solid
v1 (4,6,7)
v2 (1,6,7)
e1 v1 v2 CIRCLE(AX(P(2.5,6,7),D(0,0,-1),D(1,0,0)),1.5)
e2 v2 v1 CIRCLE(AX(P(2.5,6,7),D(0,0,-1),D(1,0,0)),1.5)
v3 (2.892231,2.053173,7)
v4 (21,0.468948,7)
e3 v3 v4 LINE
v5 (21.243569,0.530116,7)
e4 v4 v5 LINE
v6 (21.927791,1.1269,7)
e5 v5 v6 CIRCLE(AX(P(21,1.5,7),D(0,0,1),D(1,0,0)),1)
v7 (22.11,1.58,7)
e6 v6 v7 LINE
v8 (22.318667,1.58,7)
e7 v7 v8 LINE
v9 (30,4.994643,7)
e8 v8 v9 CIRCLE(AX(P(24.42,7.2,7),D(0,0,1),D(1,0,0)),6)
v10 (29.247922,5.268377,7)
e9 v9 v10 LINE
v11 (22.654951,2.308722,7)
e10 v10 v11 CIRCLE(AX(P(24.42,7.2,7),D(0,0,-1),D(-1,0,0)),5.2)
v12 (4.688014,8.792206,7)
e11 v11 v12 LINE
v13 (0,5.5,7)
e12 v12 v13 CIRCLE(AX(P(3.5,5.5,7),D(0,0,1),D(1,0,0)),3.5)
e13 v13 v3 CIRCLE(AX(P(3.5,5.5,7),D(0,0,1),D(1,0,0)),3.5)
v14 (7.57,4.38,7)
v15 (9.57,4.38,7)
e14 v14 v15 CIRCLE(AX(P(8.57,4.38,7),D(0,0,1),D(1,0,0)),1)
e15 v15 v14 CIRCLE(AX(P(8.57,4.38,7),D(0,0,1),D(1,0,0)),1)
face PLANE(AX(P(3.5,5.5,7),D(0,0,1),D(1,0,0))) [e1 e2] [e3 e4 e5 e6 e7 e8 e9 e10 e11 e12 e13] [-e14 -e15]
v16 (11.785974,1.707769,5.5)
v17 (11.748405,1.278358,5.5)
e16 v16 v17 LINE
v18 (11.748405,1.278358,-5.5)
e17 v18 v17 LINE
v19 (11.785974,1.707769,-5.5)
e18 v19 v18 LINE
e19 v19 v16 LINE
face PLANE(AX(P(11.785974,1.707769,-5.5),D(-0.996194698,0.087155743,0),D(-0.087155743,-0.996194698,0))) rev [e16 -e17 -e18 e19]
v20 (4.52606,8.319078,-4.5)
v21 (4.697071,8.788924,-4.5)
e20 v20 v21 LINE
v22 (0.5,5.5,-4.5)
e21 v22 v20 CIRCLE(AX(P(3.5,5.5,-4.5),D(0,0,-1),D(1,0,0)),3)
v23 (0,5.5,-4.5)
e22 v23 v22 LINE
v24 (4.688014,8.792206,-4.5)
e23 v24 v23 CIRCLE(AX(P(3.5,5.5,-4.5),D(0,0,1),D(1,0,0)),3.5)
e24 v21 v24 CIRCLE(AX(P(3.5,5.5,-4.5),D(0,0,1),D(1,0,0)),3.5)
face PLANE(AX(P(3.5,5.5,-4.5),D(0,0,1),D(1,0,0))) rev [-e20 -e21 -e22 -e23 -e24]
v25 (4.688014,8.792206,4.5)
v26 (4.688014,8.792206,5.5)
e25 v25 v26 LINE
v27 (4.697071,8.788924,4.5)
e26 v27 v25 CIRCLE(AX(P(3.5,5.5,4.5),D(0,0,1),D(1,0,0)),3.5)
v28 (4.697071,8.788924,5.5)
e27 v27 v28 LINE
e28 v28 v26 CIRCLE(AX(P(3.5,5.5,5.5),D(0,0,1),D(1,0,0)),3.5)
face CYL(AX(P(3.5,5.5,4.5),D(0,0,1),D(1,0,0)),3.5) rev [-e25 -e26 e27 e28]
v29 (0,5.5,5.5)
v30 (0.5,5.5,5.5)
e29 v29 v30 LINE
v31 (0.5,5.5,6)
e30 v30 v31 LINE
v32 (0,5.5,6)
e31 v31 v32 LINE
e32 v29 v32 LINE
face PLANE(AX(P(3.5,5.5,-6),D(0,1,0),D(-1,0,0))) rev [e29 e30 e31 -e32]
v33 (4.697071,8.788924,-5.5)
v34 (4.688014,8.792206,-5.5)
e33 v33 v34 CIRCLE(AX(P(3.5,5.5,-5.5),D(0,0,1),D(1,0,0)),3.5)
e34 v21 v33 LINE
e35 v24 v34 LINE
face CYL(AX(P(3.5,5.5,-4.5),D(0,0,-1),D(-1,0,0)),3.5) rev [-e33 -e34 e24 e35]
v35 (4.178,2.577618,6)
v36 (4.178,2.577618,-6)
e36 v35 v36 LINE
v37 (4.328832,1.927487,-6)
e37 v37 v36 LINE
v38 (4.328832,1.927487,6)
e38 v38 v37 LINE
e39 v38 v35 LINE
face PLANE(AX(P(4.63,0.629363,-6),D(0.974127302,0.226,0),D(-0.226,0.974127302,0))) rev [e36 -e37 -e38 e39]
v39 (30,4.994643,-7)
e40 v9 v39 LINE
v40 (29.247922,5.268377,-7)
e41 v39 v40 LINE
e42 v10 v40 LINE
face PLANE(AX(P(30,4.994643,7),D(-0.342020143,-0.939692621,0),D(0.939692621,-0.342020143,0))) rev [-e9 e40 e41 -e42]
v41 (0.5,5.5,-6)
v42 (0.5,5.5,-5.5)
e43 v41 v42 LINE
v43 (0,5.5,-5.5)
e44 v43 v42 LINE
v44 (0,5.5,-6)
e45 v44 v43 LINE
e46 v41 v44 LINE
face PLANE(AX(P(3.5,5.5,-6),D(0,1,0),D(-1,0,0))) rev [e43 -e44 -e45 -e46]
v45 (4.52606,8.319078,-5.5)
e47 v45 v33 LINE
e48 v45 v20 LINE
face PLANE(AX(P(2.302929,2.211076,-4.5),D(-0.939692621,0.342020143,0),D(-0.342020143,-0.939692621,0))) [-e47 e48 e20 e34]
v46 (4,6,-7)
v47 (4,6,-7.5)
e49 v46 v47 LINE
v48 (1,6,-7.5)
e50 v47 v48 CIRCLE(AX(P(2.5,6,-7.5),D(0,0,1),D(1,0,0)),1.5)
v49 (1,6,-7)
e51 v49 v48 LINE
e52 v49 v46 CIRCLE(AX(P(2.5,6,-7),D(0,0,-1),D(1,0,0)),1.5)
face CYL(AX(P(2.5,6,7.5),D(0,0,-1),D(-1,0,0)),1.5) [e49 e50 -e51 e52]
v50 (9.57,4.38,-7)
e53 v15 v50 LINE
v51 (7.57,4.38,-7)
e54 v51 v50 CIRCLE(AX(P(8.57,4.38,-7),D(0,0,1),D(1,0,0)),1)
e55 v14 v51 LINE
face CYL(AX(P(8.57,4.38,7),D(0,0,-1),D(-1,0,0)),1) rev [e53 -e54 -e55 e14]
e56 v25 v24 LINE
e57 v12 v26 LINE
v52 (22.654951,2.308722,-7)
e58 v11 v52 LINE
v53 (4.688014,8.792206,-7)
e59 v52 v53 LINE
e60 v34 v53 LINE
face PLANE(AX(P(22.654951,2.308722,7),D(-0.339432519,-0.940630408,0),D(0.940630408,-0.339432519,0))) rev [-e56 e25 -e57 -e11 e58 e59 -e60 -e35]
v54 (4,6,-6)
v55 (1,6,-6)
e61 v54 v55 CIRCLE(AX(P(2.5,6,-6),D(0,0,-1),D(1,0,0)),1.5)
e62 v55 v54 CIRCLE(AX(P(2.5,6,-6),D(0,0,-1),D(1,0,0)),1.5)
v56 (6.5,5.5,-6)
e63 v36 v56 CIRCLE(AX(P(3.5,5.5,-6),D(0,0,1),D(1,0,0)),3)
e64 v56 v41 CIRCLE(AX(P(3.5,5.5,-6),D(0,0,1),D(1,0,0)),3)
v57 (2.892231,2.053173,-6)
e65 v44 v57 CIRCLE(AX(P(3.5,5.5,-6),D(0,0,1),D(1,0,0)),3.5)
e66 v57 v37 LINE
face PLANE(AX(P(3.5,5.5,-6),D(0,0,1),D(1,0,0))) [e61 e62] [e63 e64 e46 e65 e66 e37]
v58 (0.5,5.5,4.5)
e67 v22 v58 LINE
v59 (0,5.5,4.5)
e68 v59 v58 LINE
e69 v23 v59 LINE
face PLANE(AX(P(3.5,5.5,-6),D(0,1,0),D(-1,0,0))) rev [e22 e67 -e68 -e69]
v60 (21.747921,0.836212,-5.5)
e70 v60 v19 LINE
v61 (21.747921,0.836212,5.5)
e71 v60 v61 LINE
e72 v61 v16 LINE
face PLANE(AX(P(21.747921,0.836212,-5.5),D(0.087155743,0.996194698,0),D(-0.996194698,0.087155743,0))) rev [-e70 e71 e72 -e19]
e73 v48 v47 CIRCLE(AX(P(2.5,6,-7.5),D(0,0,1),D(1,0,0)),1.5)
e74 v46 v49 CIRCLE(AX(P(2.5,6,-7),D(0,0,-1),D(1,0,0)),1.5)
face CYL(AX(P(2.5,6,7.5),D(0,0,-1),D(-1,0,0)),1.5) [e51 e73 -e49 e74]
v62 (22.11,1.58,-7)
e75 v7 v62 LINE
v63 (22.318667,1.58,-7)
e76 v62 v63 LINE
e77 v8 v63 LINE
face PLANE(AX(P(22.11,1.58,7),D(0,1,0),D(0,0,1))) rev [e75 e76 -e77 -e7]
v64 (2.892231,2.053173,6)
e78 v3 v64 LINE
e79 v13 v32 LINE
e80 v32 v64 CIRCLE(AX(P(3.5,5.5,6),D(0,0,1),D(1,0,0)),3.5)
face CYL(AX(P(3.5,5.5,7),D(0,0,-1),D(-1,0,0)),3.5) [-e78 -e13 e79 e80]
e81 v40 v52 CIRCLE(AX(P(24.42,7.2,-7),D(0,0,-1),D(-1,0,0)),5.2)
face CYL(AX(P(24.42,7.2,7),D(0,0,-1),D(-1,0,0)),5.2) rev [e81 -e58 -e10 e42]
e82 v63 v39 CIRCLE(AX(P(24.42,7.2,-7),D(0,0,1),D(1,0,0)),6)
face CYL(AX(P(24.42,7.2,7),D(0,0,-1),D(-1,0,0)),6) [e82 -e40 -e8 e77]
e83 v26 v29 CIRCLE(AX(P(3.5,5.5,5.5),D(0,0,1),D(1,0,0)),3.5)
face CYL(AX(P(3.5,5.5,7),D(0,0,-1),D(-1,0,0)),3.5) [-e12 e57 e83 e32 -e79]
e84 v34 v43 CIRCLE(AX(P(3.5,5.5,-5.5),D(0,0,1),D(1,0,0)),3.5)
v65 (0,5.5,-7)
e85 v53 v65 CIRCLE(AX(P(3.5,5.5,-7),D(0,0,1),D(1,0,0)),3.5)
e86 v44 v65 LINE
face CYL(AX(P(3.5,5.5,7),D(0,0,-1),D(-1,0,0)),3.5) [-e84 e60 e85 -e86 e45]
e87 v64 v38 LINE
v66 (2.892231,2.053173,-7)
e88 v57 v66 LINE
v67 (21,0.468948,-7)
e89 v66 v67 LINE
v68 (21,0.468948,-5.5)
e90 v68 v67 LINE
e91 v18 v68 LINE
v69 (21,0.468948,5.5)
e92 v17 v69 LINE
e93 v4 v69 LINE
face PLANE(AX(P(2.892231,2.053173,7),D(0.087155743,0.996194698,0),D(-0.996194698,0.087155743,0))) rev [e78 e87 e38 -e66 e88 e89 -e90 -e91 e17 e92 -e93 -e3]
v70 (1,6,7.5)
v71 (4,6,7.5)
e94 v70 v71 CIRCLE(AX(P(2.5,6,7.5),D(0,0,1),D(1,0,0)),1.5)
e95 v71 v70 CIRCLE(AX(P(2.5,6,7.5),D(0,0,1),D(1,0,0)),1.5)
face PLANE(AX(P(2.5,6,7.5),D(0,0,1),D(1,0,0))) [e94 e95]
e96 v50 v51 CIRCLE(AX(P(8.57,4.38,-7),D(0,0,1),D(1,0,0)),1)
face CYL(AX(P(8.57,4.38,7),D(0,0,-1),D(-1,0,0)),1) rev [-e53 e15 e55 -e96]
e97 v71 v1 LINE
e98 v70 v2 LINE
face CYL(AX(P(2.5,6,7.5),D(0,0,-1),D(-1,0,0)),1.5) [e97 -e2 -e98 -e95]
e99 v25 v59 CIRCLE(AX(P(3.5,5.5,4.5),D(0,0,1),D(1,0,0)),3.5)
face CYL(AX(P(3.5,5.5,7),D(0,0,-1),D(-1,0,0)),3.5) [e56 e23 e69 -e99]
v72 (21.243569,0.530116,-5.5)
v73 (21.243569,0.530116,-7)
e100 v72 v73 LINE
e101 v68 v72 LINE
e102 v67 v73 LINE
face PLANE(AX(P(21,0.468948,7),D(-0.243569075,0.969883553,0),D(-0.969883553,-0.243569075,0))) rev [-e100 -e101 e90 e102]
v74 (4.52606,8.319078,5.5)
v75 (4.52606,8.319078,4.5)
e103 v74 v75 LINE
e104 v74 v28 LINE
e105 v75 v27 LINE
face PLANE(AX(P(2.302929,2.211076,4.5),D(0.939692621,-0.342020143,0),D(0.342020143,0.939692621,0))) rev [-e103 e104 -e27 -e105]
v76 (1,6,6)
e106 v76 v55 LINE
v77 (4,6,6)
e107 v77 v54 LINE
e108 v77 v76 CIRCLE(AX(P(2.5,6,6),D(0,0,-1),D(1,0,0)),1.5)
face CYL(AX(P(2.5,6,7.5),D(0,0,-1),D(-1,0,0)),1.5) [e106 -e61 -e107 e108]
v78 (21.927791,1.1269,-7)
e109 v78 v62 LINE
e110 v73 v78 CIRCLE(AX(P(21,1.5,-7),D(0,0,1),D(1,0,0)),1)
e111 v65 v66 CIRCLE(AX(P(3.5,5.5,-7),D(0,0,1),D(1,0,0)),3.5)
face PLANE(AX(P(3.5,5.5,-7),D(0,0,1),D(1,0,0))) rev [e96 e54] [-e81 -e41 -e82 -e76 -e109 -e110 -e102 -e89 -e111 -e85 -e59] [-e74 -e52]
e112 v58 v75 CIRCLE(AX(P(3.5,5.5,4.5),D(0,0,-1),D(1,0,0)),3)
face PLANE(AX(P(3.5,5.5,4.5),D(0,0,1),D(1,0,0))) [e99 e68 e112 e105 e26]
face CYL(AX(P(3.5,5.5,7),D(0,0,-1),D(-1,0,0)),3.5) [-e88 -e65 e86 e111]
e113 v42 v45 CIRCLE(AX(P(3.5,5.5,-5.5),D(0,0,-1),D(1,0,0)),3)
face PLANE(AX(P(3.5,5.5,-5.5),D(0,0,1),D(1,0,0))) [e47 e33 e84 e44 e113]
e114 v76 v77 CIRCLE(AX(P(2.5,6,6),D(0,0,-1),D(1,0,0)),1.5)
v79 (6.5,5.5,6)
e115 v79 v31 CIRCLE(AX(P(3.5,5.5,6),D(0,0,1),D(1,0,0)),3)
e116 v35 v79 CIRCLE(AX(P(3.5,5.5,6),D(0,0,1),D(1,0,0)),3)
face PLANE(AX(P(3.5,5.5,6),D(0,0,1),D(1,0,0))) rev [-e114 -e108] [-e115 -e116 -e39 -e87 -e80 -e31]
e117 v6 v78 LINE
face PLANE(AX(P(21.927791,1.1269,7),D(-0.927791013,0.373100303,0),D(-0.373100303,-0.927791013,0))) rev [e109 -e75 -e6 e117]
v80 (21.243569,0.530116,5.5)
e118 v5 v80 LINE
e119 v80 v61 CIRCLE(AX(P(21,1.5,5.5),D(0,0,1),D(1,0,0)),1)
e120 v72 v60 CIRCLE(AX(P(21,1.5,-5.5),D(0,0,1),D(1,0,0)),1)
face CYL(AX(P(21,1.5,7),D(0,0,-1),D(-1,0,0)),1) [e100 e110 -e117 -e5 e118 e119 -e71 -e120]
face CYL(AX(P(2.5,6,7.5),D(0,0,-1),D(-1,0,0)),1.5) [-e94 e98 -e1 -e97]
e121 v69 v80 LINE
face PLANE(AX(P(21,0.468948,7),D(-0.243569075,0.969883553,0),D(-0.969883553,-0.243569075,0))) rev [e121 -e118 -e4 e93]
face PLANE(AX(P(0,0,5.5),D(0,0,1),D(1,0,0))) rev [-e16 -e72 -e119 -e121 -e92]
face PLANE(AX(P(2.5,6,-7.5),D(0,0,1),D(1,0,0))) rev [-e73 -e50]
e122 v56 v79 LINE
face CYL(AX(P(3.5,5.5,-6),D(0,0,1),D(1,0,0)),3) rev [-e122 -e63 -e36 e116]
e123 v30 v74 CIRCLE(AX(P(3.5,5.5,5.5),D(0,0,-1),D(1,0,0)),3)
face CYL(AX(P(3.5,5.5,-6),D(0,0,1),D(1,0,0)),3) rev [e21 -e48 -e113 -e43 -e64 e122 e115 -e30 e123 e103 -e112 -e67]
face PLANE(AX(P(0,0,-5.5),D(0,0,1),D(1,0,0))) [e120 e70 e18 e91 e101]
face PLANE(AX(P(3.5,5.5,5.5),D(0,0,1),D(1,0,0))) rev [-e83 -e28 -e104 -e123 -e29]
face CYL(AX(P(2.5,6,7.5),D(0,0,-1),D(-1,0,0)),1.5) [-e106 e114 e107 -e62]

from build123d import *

# Parameters (mm, degrees)
BOSS_EXTRUDE1_DEPTH      = 7
BOSS_EXTRUDE1_DEPTH_BACK = 7
SKETCH1_R                = 1
CUT_EXTRUDE1_DEPTH       = 6
CUT_EXTRUDE1_DEPTH_BACK  = 6
CUT_EXTRUDE2_DEPTH       = 6
CUT_EXTRUDE2_DEPTH_BACK  = 6
SKETCH3_R                = 3
CUT_EXTRUDE3_START       = -1
CUT_EXTRUDE3_DEPTH       = 1
CUT_EXTRUDE4_DEPTH       = 1
BOSS_EXTRUDE2_DEPTH      = 7.5
BOSS_EXTRUDE2_DEPTH_BACK = 7.5
SKETCH6_R                = 1.5
CUT_EXTRUDE5_DEPTH       = 5.5
CUT_EXTRUDE5_DEPTH_BACK  = 5.5


with BuildPart() as part:
    # Sketch1 → Boss-Extrude1 (new, two sides: drawn at the far end of the back side and taken through both)
    with BuildSketch(Plane.XY.offset(-BOSS_EXTRUDE1_DEPTH_BACK)):
        with BuildLine():
            Line((2.892231378, 2.053172864), (21, 0.468948388))
            Line((21, 0.468948388), (21.243569075, 0.530116447))
            ThreePointArc((21.243569075, 0.530116447), (21.657311704, 0.746381181), (21.927791013, 1.126899697))
            Line((21.927791013, 1.126899697), (22.11, 1.58))
            Line((22.11, 1.58), (22.31866709, 1.58))
            ThreePointArc((22.31866709, 1.58), (26.857258232, 1.7173207), (30, 4.994642886))
            Line((30, 4.994642886), (29.24792212, 5.268376848))
            ThreePointArc((29.24792212, 5.268376848), (26.549597889, 2.45607622), (22.654950899, 2.308721878))
            Line((22.654950899, 2.308721878), (4.688013818, 8.792206429))
            ThreePointArc((4.688013818, 8.792206429), (0.118016194, 6.401213367), (2.892231378, 2.053172864))
        make_face()
        with Locations((8.57, 4.38)):
            Circle(SKETCH1_R, mode=Mode.SUBTRACT)
    extrude(amount=BOSS_EXTRUDE1_DEPTH + BOSS_EXTRUDE1_DEPTH_BACK)

    # Sketch2 → Cut-Extrude1 (cut, two sides: drawn at the far end of the back side and taken through both)
    with BuildSketch(Plane.XY.offset(-CUT_EXTRUDE1_DEPTH_BACK)):
        with BuildLine():
            Line((4.63, 0.629363491), (3.5, 5.5))
            Line((3.5, 5.5), (-1.5, 5.5))
            ThreePointArc((-1.5, 5.5), (0.389533797, 1.585284174), (4.63, 0.629363491))
        make_face()
    extrude(amount=CUT_EXTRUDE1_DEPTH + CUT_EXTRUDE1_DEPTH_BACK, mode=Mode.SUBTRACT)

    # Sketch3 → Cut-Extrude2 (cut, two sides: drawn at the far end of the back side and taken through both)
    with BuildSketch(Plane.XY.offset(-CUT_EXTRUDE2_DEPTH_BACK)):
        with Locations((3.5, 5.5)):
            Circle(SKETCH3_R)
    extrude(amount=CUT_EXTRUDE2_DEPTH + CUT_EXTRUDE2_DEPTH_BACK, mode=Mode.SUBTRACT)

    # Sketch4 → Cut-Extrude3 (cut)
    with BuildSketch(Plane.XY.offset(5.5).offset(CUT_EXTRUDE3_START)):
        with BuildLine():
            Line((2.302929498, 2.211075827), (4.697070502, 8.788924173))
            ThreePointArc((4.697070502, 8.788924173), (0.211075827, 6.697070502), (2.302929498, 2.211075827))
        make_face()
    extrude(amount=CUT_EXTRUDE3_DEPTH, mode=Mode.SUBTRACT)

    # Sketch5 → Cut-Extrude4 (cut)
    with BuildSketch(Plane.XY.offset(-5.5)):
        with BuildLine():
            Line((2.302929498, 2.211075827), (4.697070502, 8.788924173))
            ThreePointArc((4.697070502, 8.788924173), (0.211075827, 6.697070502), (2.302929498, 2.211075827))
        make_face()
    extrude(amount=CUT_EXTRUDE4_DEPTH, mode=Mode.SUBTRACT)

    # Sketch6 → Boss-Extrude2 (add, two sides: drawn at the far end of the back side and taken through both)
    with BuildSketch(Plane.XY.offset(-BOSS_EXTRUDE2_DEPTH_BACK)):
        with Locations((2.5, 6)):
            Circle(SKETCH6_R)
    extrude(amount=BOSS_EXTRUDE2_DEPTH + BOSS_EXTRUDE2_DEPTH_BACK)

    # Sketch7 → Cut-Extrude5 (cut, two sides: drawn at the far end of the back side and taken through both)
    with BuildSketch(Plane.XY.offset(-CUT_EXTRUDE5_DEPTH_BACK)):
        Polygon((11.724964743, 1.0104331), (21.686911724, 0.138875672), (21.747920744, 0.836211961), (11.785973763, 1.707769388), align=None)
    extrude(amount=CUT_EXTRUDE5_DEPTH + CUT_EXTRUDE5_DEPTH_BACK, mode=Mode.SUBTRACT)


solid = part.part
